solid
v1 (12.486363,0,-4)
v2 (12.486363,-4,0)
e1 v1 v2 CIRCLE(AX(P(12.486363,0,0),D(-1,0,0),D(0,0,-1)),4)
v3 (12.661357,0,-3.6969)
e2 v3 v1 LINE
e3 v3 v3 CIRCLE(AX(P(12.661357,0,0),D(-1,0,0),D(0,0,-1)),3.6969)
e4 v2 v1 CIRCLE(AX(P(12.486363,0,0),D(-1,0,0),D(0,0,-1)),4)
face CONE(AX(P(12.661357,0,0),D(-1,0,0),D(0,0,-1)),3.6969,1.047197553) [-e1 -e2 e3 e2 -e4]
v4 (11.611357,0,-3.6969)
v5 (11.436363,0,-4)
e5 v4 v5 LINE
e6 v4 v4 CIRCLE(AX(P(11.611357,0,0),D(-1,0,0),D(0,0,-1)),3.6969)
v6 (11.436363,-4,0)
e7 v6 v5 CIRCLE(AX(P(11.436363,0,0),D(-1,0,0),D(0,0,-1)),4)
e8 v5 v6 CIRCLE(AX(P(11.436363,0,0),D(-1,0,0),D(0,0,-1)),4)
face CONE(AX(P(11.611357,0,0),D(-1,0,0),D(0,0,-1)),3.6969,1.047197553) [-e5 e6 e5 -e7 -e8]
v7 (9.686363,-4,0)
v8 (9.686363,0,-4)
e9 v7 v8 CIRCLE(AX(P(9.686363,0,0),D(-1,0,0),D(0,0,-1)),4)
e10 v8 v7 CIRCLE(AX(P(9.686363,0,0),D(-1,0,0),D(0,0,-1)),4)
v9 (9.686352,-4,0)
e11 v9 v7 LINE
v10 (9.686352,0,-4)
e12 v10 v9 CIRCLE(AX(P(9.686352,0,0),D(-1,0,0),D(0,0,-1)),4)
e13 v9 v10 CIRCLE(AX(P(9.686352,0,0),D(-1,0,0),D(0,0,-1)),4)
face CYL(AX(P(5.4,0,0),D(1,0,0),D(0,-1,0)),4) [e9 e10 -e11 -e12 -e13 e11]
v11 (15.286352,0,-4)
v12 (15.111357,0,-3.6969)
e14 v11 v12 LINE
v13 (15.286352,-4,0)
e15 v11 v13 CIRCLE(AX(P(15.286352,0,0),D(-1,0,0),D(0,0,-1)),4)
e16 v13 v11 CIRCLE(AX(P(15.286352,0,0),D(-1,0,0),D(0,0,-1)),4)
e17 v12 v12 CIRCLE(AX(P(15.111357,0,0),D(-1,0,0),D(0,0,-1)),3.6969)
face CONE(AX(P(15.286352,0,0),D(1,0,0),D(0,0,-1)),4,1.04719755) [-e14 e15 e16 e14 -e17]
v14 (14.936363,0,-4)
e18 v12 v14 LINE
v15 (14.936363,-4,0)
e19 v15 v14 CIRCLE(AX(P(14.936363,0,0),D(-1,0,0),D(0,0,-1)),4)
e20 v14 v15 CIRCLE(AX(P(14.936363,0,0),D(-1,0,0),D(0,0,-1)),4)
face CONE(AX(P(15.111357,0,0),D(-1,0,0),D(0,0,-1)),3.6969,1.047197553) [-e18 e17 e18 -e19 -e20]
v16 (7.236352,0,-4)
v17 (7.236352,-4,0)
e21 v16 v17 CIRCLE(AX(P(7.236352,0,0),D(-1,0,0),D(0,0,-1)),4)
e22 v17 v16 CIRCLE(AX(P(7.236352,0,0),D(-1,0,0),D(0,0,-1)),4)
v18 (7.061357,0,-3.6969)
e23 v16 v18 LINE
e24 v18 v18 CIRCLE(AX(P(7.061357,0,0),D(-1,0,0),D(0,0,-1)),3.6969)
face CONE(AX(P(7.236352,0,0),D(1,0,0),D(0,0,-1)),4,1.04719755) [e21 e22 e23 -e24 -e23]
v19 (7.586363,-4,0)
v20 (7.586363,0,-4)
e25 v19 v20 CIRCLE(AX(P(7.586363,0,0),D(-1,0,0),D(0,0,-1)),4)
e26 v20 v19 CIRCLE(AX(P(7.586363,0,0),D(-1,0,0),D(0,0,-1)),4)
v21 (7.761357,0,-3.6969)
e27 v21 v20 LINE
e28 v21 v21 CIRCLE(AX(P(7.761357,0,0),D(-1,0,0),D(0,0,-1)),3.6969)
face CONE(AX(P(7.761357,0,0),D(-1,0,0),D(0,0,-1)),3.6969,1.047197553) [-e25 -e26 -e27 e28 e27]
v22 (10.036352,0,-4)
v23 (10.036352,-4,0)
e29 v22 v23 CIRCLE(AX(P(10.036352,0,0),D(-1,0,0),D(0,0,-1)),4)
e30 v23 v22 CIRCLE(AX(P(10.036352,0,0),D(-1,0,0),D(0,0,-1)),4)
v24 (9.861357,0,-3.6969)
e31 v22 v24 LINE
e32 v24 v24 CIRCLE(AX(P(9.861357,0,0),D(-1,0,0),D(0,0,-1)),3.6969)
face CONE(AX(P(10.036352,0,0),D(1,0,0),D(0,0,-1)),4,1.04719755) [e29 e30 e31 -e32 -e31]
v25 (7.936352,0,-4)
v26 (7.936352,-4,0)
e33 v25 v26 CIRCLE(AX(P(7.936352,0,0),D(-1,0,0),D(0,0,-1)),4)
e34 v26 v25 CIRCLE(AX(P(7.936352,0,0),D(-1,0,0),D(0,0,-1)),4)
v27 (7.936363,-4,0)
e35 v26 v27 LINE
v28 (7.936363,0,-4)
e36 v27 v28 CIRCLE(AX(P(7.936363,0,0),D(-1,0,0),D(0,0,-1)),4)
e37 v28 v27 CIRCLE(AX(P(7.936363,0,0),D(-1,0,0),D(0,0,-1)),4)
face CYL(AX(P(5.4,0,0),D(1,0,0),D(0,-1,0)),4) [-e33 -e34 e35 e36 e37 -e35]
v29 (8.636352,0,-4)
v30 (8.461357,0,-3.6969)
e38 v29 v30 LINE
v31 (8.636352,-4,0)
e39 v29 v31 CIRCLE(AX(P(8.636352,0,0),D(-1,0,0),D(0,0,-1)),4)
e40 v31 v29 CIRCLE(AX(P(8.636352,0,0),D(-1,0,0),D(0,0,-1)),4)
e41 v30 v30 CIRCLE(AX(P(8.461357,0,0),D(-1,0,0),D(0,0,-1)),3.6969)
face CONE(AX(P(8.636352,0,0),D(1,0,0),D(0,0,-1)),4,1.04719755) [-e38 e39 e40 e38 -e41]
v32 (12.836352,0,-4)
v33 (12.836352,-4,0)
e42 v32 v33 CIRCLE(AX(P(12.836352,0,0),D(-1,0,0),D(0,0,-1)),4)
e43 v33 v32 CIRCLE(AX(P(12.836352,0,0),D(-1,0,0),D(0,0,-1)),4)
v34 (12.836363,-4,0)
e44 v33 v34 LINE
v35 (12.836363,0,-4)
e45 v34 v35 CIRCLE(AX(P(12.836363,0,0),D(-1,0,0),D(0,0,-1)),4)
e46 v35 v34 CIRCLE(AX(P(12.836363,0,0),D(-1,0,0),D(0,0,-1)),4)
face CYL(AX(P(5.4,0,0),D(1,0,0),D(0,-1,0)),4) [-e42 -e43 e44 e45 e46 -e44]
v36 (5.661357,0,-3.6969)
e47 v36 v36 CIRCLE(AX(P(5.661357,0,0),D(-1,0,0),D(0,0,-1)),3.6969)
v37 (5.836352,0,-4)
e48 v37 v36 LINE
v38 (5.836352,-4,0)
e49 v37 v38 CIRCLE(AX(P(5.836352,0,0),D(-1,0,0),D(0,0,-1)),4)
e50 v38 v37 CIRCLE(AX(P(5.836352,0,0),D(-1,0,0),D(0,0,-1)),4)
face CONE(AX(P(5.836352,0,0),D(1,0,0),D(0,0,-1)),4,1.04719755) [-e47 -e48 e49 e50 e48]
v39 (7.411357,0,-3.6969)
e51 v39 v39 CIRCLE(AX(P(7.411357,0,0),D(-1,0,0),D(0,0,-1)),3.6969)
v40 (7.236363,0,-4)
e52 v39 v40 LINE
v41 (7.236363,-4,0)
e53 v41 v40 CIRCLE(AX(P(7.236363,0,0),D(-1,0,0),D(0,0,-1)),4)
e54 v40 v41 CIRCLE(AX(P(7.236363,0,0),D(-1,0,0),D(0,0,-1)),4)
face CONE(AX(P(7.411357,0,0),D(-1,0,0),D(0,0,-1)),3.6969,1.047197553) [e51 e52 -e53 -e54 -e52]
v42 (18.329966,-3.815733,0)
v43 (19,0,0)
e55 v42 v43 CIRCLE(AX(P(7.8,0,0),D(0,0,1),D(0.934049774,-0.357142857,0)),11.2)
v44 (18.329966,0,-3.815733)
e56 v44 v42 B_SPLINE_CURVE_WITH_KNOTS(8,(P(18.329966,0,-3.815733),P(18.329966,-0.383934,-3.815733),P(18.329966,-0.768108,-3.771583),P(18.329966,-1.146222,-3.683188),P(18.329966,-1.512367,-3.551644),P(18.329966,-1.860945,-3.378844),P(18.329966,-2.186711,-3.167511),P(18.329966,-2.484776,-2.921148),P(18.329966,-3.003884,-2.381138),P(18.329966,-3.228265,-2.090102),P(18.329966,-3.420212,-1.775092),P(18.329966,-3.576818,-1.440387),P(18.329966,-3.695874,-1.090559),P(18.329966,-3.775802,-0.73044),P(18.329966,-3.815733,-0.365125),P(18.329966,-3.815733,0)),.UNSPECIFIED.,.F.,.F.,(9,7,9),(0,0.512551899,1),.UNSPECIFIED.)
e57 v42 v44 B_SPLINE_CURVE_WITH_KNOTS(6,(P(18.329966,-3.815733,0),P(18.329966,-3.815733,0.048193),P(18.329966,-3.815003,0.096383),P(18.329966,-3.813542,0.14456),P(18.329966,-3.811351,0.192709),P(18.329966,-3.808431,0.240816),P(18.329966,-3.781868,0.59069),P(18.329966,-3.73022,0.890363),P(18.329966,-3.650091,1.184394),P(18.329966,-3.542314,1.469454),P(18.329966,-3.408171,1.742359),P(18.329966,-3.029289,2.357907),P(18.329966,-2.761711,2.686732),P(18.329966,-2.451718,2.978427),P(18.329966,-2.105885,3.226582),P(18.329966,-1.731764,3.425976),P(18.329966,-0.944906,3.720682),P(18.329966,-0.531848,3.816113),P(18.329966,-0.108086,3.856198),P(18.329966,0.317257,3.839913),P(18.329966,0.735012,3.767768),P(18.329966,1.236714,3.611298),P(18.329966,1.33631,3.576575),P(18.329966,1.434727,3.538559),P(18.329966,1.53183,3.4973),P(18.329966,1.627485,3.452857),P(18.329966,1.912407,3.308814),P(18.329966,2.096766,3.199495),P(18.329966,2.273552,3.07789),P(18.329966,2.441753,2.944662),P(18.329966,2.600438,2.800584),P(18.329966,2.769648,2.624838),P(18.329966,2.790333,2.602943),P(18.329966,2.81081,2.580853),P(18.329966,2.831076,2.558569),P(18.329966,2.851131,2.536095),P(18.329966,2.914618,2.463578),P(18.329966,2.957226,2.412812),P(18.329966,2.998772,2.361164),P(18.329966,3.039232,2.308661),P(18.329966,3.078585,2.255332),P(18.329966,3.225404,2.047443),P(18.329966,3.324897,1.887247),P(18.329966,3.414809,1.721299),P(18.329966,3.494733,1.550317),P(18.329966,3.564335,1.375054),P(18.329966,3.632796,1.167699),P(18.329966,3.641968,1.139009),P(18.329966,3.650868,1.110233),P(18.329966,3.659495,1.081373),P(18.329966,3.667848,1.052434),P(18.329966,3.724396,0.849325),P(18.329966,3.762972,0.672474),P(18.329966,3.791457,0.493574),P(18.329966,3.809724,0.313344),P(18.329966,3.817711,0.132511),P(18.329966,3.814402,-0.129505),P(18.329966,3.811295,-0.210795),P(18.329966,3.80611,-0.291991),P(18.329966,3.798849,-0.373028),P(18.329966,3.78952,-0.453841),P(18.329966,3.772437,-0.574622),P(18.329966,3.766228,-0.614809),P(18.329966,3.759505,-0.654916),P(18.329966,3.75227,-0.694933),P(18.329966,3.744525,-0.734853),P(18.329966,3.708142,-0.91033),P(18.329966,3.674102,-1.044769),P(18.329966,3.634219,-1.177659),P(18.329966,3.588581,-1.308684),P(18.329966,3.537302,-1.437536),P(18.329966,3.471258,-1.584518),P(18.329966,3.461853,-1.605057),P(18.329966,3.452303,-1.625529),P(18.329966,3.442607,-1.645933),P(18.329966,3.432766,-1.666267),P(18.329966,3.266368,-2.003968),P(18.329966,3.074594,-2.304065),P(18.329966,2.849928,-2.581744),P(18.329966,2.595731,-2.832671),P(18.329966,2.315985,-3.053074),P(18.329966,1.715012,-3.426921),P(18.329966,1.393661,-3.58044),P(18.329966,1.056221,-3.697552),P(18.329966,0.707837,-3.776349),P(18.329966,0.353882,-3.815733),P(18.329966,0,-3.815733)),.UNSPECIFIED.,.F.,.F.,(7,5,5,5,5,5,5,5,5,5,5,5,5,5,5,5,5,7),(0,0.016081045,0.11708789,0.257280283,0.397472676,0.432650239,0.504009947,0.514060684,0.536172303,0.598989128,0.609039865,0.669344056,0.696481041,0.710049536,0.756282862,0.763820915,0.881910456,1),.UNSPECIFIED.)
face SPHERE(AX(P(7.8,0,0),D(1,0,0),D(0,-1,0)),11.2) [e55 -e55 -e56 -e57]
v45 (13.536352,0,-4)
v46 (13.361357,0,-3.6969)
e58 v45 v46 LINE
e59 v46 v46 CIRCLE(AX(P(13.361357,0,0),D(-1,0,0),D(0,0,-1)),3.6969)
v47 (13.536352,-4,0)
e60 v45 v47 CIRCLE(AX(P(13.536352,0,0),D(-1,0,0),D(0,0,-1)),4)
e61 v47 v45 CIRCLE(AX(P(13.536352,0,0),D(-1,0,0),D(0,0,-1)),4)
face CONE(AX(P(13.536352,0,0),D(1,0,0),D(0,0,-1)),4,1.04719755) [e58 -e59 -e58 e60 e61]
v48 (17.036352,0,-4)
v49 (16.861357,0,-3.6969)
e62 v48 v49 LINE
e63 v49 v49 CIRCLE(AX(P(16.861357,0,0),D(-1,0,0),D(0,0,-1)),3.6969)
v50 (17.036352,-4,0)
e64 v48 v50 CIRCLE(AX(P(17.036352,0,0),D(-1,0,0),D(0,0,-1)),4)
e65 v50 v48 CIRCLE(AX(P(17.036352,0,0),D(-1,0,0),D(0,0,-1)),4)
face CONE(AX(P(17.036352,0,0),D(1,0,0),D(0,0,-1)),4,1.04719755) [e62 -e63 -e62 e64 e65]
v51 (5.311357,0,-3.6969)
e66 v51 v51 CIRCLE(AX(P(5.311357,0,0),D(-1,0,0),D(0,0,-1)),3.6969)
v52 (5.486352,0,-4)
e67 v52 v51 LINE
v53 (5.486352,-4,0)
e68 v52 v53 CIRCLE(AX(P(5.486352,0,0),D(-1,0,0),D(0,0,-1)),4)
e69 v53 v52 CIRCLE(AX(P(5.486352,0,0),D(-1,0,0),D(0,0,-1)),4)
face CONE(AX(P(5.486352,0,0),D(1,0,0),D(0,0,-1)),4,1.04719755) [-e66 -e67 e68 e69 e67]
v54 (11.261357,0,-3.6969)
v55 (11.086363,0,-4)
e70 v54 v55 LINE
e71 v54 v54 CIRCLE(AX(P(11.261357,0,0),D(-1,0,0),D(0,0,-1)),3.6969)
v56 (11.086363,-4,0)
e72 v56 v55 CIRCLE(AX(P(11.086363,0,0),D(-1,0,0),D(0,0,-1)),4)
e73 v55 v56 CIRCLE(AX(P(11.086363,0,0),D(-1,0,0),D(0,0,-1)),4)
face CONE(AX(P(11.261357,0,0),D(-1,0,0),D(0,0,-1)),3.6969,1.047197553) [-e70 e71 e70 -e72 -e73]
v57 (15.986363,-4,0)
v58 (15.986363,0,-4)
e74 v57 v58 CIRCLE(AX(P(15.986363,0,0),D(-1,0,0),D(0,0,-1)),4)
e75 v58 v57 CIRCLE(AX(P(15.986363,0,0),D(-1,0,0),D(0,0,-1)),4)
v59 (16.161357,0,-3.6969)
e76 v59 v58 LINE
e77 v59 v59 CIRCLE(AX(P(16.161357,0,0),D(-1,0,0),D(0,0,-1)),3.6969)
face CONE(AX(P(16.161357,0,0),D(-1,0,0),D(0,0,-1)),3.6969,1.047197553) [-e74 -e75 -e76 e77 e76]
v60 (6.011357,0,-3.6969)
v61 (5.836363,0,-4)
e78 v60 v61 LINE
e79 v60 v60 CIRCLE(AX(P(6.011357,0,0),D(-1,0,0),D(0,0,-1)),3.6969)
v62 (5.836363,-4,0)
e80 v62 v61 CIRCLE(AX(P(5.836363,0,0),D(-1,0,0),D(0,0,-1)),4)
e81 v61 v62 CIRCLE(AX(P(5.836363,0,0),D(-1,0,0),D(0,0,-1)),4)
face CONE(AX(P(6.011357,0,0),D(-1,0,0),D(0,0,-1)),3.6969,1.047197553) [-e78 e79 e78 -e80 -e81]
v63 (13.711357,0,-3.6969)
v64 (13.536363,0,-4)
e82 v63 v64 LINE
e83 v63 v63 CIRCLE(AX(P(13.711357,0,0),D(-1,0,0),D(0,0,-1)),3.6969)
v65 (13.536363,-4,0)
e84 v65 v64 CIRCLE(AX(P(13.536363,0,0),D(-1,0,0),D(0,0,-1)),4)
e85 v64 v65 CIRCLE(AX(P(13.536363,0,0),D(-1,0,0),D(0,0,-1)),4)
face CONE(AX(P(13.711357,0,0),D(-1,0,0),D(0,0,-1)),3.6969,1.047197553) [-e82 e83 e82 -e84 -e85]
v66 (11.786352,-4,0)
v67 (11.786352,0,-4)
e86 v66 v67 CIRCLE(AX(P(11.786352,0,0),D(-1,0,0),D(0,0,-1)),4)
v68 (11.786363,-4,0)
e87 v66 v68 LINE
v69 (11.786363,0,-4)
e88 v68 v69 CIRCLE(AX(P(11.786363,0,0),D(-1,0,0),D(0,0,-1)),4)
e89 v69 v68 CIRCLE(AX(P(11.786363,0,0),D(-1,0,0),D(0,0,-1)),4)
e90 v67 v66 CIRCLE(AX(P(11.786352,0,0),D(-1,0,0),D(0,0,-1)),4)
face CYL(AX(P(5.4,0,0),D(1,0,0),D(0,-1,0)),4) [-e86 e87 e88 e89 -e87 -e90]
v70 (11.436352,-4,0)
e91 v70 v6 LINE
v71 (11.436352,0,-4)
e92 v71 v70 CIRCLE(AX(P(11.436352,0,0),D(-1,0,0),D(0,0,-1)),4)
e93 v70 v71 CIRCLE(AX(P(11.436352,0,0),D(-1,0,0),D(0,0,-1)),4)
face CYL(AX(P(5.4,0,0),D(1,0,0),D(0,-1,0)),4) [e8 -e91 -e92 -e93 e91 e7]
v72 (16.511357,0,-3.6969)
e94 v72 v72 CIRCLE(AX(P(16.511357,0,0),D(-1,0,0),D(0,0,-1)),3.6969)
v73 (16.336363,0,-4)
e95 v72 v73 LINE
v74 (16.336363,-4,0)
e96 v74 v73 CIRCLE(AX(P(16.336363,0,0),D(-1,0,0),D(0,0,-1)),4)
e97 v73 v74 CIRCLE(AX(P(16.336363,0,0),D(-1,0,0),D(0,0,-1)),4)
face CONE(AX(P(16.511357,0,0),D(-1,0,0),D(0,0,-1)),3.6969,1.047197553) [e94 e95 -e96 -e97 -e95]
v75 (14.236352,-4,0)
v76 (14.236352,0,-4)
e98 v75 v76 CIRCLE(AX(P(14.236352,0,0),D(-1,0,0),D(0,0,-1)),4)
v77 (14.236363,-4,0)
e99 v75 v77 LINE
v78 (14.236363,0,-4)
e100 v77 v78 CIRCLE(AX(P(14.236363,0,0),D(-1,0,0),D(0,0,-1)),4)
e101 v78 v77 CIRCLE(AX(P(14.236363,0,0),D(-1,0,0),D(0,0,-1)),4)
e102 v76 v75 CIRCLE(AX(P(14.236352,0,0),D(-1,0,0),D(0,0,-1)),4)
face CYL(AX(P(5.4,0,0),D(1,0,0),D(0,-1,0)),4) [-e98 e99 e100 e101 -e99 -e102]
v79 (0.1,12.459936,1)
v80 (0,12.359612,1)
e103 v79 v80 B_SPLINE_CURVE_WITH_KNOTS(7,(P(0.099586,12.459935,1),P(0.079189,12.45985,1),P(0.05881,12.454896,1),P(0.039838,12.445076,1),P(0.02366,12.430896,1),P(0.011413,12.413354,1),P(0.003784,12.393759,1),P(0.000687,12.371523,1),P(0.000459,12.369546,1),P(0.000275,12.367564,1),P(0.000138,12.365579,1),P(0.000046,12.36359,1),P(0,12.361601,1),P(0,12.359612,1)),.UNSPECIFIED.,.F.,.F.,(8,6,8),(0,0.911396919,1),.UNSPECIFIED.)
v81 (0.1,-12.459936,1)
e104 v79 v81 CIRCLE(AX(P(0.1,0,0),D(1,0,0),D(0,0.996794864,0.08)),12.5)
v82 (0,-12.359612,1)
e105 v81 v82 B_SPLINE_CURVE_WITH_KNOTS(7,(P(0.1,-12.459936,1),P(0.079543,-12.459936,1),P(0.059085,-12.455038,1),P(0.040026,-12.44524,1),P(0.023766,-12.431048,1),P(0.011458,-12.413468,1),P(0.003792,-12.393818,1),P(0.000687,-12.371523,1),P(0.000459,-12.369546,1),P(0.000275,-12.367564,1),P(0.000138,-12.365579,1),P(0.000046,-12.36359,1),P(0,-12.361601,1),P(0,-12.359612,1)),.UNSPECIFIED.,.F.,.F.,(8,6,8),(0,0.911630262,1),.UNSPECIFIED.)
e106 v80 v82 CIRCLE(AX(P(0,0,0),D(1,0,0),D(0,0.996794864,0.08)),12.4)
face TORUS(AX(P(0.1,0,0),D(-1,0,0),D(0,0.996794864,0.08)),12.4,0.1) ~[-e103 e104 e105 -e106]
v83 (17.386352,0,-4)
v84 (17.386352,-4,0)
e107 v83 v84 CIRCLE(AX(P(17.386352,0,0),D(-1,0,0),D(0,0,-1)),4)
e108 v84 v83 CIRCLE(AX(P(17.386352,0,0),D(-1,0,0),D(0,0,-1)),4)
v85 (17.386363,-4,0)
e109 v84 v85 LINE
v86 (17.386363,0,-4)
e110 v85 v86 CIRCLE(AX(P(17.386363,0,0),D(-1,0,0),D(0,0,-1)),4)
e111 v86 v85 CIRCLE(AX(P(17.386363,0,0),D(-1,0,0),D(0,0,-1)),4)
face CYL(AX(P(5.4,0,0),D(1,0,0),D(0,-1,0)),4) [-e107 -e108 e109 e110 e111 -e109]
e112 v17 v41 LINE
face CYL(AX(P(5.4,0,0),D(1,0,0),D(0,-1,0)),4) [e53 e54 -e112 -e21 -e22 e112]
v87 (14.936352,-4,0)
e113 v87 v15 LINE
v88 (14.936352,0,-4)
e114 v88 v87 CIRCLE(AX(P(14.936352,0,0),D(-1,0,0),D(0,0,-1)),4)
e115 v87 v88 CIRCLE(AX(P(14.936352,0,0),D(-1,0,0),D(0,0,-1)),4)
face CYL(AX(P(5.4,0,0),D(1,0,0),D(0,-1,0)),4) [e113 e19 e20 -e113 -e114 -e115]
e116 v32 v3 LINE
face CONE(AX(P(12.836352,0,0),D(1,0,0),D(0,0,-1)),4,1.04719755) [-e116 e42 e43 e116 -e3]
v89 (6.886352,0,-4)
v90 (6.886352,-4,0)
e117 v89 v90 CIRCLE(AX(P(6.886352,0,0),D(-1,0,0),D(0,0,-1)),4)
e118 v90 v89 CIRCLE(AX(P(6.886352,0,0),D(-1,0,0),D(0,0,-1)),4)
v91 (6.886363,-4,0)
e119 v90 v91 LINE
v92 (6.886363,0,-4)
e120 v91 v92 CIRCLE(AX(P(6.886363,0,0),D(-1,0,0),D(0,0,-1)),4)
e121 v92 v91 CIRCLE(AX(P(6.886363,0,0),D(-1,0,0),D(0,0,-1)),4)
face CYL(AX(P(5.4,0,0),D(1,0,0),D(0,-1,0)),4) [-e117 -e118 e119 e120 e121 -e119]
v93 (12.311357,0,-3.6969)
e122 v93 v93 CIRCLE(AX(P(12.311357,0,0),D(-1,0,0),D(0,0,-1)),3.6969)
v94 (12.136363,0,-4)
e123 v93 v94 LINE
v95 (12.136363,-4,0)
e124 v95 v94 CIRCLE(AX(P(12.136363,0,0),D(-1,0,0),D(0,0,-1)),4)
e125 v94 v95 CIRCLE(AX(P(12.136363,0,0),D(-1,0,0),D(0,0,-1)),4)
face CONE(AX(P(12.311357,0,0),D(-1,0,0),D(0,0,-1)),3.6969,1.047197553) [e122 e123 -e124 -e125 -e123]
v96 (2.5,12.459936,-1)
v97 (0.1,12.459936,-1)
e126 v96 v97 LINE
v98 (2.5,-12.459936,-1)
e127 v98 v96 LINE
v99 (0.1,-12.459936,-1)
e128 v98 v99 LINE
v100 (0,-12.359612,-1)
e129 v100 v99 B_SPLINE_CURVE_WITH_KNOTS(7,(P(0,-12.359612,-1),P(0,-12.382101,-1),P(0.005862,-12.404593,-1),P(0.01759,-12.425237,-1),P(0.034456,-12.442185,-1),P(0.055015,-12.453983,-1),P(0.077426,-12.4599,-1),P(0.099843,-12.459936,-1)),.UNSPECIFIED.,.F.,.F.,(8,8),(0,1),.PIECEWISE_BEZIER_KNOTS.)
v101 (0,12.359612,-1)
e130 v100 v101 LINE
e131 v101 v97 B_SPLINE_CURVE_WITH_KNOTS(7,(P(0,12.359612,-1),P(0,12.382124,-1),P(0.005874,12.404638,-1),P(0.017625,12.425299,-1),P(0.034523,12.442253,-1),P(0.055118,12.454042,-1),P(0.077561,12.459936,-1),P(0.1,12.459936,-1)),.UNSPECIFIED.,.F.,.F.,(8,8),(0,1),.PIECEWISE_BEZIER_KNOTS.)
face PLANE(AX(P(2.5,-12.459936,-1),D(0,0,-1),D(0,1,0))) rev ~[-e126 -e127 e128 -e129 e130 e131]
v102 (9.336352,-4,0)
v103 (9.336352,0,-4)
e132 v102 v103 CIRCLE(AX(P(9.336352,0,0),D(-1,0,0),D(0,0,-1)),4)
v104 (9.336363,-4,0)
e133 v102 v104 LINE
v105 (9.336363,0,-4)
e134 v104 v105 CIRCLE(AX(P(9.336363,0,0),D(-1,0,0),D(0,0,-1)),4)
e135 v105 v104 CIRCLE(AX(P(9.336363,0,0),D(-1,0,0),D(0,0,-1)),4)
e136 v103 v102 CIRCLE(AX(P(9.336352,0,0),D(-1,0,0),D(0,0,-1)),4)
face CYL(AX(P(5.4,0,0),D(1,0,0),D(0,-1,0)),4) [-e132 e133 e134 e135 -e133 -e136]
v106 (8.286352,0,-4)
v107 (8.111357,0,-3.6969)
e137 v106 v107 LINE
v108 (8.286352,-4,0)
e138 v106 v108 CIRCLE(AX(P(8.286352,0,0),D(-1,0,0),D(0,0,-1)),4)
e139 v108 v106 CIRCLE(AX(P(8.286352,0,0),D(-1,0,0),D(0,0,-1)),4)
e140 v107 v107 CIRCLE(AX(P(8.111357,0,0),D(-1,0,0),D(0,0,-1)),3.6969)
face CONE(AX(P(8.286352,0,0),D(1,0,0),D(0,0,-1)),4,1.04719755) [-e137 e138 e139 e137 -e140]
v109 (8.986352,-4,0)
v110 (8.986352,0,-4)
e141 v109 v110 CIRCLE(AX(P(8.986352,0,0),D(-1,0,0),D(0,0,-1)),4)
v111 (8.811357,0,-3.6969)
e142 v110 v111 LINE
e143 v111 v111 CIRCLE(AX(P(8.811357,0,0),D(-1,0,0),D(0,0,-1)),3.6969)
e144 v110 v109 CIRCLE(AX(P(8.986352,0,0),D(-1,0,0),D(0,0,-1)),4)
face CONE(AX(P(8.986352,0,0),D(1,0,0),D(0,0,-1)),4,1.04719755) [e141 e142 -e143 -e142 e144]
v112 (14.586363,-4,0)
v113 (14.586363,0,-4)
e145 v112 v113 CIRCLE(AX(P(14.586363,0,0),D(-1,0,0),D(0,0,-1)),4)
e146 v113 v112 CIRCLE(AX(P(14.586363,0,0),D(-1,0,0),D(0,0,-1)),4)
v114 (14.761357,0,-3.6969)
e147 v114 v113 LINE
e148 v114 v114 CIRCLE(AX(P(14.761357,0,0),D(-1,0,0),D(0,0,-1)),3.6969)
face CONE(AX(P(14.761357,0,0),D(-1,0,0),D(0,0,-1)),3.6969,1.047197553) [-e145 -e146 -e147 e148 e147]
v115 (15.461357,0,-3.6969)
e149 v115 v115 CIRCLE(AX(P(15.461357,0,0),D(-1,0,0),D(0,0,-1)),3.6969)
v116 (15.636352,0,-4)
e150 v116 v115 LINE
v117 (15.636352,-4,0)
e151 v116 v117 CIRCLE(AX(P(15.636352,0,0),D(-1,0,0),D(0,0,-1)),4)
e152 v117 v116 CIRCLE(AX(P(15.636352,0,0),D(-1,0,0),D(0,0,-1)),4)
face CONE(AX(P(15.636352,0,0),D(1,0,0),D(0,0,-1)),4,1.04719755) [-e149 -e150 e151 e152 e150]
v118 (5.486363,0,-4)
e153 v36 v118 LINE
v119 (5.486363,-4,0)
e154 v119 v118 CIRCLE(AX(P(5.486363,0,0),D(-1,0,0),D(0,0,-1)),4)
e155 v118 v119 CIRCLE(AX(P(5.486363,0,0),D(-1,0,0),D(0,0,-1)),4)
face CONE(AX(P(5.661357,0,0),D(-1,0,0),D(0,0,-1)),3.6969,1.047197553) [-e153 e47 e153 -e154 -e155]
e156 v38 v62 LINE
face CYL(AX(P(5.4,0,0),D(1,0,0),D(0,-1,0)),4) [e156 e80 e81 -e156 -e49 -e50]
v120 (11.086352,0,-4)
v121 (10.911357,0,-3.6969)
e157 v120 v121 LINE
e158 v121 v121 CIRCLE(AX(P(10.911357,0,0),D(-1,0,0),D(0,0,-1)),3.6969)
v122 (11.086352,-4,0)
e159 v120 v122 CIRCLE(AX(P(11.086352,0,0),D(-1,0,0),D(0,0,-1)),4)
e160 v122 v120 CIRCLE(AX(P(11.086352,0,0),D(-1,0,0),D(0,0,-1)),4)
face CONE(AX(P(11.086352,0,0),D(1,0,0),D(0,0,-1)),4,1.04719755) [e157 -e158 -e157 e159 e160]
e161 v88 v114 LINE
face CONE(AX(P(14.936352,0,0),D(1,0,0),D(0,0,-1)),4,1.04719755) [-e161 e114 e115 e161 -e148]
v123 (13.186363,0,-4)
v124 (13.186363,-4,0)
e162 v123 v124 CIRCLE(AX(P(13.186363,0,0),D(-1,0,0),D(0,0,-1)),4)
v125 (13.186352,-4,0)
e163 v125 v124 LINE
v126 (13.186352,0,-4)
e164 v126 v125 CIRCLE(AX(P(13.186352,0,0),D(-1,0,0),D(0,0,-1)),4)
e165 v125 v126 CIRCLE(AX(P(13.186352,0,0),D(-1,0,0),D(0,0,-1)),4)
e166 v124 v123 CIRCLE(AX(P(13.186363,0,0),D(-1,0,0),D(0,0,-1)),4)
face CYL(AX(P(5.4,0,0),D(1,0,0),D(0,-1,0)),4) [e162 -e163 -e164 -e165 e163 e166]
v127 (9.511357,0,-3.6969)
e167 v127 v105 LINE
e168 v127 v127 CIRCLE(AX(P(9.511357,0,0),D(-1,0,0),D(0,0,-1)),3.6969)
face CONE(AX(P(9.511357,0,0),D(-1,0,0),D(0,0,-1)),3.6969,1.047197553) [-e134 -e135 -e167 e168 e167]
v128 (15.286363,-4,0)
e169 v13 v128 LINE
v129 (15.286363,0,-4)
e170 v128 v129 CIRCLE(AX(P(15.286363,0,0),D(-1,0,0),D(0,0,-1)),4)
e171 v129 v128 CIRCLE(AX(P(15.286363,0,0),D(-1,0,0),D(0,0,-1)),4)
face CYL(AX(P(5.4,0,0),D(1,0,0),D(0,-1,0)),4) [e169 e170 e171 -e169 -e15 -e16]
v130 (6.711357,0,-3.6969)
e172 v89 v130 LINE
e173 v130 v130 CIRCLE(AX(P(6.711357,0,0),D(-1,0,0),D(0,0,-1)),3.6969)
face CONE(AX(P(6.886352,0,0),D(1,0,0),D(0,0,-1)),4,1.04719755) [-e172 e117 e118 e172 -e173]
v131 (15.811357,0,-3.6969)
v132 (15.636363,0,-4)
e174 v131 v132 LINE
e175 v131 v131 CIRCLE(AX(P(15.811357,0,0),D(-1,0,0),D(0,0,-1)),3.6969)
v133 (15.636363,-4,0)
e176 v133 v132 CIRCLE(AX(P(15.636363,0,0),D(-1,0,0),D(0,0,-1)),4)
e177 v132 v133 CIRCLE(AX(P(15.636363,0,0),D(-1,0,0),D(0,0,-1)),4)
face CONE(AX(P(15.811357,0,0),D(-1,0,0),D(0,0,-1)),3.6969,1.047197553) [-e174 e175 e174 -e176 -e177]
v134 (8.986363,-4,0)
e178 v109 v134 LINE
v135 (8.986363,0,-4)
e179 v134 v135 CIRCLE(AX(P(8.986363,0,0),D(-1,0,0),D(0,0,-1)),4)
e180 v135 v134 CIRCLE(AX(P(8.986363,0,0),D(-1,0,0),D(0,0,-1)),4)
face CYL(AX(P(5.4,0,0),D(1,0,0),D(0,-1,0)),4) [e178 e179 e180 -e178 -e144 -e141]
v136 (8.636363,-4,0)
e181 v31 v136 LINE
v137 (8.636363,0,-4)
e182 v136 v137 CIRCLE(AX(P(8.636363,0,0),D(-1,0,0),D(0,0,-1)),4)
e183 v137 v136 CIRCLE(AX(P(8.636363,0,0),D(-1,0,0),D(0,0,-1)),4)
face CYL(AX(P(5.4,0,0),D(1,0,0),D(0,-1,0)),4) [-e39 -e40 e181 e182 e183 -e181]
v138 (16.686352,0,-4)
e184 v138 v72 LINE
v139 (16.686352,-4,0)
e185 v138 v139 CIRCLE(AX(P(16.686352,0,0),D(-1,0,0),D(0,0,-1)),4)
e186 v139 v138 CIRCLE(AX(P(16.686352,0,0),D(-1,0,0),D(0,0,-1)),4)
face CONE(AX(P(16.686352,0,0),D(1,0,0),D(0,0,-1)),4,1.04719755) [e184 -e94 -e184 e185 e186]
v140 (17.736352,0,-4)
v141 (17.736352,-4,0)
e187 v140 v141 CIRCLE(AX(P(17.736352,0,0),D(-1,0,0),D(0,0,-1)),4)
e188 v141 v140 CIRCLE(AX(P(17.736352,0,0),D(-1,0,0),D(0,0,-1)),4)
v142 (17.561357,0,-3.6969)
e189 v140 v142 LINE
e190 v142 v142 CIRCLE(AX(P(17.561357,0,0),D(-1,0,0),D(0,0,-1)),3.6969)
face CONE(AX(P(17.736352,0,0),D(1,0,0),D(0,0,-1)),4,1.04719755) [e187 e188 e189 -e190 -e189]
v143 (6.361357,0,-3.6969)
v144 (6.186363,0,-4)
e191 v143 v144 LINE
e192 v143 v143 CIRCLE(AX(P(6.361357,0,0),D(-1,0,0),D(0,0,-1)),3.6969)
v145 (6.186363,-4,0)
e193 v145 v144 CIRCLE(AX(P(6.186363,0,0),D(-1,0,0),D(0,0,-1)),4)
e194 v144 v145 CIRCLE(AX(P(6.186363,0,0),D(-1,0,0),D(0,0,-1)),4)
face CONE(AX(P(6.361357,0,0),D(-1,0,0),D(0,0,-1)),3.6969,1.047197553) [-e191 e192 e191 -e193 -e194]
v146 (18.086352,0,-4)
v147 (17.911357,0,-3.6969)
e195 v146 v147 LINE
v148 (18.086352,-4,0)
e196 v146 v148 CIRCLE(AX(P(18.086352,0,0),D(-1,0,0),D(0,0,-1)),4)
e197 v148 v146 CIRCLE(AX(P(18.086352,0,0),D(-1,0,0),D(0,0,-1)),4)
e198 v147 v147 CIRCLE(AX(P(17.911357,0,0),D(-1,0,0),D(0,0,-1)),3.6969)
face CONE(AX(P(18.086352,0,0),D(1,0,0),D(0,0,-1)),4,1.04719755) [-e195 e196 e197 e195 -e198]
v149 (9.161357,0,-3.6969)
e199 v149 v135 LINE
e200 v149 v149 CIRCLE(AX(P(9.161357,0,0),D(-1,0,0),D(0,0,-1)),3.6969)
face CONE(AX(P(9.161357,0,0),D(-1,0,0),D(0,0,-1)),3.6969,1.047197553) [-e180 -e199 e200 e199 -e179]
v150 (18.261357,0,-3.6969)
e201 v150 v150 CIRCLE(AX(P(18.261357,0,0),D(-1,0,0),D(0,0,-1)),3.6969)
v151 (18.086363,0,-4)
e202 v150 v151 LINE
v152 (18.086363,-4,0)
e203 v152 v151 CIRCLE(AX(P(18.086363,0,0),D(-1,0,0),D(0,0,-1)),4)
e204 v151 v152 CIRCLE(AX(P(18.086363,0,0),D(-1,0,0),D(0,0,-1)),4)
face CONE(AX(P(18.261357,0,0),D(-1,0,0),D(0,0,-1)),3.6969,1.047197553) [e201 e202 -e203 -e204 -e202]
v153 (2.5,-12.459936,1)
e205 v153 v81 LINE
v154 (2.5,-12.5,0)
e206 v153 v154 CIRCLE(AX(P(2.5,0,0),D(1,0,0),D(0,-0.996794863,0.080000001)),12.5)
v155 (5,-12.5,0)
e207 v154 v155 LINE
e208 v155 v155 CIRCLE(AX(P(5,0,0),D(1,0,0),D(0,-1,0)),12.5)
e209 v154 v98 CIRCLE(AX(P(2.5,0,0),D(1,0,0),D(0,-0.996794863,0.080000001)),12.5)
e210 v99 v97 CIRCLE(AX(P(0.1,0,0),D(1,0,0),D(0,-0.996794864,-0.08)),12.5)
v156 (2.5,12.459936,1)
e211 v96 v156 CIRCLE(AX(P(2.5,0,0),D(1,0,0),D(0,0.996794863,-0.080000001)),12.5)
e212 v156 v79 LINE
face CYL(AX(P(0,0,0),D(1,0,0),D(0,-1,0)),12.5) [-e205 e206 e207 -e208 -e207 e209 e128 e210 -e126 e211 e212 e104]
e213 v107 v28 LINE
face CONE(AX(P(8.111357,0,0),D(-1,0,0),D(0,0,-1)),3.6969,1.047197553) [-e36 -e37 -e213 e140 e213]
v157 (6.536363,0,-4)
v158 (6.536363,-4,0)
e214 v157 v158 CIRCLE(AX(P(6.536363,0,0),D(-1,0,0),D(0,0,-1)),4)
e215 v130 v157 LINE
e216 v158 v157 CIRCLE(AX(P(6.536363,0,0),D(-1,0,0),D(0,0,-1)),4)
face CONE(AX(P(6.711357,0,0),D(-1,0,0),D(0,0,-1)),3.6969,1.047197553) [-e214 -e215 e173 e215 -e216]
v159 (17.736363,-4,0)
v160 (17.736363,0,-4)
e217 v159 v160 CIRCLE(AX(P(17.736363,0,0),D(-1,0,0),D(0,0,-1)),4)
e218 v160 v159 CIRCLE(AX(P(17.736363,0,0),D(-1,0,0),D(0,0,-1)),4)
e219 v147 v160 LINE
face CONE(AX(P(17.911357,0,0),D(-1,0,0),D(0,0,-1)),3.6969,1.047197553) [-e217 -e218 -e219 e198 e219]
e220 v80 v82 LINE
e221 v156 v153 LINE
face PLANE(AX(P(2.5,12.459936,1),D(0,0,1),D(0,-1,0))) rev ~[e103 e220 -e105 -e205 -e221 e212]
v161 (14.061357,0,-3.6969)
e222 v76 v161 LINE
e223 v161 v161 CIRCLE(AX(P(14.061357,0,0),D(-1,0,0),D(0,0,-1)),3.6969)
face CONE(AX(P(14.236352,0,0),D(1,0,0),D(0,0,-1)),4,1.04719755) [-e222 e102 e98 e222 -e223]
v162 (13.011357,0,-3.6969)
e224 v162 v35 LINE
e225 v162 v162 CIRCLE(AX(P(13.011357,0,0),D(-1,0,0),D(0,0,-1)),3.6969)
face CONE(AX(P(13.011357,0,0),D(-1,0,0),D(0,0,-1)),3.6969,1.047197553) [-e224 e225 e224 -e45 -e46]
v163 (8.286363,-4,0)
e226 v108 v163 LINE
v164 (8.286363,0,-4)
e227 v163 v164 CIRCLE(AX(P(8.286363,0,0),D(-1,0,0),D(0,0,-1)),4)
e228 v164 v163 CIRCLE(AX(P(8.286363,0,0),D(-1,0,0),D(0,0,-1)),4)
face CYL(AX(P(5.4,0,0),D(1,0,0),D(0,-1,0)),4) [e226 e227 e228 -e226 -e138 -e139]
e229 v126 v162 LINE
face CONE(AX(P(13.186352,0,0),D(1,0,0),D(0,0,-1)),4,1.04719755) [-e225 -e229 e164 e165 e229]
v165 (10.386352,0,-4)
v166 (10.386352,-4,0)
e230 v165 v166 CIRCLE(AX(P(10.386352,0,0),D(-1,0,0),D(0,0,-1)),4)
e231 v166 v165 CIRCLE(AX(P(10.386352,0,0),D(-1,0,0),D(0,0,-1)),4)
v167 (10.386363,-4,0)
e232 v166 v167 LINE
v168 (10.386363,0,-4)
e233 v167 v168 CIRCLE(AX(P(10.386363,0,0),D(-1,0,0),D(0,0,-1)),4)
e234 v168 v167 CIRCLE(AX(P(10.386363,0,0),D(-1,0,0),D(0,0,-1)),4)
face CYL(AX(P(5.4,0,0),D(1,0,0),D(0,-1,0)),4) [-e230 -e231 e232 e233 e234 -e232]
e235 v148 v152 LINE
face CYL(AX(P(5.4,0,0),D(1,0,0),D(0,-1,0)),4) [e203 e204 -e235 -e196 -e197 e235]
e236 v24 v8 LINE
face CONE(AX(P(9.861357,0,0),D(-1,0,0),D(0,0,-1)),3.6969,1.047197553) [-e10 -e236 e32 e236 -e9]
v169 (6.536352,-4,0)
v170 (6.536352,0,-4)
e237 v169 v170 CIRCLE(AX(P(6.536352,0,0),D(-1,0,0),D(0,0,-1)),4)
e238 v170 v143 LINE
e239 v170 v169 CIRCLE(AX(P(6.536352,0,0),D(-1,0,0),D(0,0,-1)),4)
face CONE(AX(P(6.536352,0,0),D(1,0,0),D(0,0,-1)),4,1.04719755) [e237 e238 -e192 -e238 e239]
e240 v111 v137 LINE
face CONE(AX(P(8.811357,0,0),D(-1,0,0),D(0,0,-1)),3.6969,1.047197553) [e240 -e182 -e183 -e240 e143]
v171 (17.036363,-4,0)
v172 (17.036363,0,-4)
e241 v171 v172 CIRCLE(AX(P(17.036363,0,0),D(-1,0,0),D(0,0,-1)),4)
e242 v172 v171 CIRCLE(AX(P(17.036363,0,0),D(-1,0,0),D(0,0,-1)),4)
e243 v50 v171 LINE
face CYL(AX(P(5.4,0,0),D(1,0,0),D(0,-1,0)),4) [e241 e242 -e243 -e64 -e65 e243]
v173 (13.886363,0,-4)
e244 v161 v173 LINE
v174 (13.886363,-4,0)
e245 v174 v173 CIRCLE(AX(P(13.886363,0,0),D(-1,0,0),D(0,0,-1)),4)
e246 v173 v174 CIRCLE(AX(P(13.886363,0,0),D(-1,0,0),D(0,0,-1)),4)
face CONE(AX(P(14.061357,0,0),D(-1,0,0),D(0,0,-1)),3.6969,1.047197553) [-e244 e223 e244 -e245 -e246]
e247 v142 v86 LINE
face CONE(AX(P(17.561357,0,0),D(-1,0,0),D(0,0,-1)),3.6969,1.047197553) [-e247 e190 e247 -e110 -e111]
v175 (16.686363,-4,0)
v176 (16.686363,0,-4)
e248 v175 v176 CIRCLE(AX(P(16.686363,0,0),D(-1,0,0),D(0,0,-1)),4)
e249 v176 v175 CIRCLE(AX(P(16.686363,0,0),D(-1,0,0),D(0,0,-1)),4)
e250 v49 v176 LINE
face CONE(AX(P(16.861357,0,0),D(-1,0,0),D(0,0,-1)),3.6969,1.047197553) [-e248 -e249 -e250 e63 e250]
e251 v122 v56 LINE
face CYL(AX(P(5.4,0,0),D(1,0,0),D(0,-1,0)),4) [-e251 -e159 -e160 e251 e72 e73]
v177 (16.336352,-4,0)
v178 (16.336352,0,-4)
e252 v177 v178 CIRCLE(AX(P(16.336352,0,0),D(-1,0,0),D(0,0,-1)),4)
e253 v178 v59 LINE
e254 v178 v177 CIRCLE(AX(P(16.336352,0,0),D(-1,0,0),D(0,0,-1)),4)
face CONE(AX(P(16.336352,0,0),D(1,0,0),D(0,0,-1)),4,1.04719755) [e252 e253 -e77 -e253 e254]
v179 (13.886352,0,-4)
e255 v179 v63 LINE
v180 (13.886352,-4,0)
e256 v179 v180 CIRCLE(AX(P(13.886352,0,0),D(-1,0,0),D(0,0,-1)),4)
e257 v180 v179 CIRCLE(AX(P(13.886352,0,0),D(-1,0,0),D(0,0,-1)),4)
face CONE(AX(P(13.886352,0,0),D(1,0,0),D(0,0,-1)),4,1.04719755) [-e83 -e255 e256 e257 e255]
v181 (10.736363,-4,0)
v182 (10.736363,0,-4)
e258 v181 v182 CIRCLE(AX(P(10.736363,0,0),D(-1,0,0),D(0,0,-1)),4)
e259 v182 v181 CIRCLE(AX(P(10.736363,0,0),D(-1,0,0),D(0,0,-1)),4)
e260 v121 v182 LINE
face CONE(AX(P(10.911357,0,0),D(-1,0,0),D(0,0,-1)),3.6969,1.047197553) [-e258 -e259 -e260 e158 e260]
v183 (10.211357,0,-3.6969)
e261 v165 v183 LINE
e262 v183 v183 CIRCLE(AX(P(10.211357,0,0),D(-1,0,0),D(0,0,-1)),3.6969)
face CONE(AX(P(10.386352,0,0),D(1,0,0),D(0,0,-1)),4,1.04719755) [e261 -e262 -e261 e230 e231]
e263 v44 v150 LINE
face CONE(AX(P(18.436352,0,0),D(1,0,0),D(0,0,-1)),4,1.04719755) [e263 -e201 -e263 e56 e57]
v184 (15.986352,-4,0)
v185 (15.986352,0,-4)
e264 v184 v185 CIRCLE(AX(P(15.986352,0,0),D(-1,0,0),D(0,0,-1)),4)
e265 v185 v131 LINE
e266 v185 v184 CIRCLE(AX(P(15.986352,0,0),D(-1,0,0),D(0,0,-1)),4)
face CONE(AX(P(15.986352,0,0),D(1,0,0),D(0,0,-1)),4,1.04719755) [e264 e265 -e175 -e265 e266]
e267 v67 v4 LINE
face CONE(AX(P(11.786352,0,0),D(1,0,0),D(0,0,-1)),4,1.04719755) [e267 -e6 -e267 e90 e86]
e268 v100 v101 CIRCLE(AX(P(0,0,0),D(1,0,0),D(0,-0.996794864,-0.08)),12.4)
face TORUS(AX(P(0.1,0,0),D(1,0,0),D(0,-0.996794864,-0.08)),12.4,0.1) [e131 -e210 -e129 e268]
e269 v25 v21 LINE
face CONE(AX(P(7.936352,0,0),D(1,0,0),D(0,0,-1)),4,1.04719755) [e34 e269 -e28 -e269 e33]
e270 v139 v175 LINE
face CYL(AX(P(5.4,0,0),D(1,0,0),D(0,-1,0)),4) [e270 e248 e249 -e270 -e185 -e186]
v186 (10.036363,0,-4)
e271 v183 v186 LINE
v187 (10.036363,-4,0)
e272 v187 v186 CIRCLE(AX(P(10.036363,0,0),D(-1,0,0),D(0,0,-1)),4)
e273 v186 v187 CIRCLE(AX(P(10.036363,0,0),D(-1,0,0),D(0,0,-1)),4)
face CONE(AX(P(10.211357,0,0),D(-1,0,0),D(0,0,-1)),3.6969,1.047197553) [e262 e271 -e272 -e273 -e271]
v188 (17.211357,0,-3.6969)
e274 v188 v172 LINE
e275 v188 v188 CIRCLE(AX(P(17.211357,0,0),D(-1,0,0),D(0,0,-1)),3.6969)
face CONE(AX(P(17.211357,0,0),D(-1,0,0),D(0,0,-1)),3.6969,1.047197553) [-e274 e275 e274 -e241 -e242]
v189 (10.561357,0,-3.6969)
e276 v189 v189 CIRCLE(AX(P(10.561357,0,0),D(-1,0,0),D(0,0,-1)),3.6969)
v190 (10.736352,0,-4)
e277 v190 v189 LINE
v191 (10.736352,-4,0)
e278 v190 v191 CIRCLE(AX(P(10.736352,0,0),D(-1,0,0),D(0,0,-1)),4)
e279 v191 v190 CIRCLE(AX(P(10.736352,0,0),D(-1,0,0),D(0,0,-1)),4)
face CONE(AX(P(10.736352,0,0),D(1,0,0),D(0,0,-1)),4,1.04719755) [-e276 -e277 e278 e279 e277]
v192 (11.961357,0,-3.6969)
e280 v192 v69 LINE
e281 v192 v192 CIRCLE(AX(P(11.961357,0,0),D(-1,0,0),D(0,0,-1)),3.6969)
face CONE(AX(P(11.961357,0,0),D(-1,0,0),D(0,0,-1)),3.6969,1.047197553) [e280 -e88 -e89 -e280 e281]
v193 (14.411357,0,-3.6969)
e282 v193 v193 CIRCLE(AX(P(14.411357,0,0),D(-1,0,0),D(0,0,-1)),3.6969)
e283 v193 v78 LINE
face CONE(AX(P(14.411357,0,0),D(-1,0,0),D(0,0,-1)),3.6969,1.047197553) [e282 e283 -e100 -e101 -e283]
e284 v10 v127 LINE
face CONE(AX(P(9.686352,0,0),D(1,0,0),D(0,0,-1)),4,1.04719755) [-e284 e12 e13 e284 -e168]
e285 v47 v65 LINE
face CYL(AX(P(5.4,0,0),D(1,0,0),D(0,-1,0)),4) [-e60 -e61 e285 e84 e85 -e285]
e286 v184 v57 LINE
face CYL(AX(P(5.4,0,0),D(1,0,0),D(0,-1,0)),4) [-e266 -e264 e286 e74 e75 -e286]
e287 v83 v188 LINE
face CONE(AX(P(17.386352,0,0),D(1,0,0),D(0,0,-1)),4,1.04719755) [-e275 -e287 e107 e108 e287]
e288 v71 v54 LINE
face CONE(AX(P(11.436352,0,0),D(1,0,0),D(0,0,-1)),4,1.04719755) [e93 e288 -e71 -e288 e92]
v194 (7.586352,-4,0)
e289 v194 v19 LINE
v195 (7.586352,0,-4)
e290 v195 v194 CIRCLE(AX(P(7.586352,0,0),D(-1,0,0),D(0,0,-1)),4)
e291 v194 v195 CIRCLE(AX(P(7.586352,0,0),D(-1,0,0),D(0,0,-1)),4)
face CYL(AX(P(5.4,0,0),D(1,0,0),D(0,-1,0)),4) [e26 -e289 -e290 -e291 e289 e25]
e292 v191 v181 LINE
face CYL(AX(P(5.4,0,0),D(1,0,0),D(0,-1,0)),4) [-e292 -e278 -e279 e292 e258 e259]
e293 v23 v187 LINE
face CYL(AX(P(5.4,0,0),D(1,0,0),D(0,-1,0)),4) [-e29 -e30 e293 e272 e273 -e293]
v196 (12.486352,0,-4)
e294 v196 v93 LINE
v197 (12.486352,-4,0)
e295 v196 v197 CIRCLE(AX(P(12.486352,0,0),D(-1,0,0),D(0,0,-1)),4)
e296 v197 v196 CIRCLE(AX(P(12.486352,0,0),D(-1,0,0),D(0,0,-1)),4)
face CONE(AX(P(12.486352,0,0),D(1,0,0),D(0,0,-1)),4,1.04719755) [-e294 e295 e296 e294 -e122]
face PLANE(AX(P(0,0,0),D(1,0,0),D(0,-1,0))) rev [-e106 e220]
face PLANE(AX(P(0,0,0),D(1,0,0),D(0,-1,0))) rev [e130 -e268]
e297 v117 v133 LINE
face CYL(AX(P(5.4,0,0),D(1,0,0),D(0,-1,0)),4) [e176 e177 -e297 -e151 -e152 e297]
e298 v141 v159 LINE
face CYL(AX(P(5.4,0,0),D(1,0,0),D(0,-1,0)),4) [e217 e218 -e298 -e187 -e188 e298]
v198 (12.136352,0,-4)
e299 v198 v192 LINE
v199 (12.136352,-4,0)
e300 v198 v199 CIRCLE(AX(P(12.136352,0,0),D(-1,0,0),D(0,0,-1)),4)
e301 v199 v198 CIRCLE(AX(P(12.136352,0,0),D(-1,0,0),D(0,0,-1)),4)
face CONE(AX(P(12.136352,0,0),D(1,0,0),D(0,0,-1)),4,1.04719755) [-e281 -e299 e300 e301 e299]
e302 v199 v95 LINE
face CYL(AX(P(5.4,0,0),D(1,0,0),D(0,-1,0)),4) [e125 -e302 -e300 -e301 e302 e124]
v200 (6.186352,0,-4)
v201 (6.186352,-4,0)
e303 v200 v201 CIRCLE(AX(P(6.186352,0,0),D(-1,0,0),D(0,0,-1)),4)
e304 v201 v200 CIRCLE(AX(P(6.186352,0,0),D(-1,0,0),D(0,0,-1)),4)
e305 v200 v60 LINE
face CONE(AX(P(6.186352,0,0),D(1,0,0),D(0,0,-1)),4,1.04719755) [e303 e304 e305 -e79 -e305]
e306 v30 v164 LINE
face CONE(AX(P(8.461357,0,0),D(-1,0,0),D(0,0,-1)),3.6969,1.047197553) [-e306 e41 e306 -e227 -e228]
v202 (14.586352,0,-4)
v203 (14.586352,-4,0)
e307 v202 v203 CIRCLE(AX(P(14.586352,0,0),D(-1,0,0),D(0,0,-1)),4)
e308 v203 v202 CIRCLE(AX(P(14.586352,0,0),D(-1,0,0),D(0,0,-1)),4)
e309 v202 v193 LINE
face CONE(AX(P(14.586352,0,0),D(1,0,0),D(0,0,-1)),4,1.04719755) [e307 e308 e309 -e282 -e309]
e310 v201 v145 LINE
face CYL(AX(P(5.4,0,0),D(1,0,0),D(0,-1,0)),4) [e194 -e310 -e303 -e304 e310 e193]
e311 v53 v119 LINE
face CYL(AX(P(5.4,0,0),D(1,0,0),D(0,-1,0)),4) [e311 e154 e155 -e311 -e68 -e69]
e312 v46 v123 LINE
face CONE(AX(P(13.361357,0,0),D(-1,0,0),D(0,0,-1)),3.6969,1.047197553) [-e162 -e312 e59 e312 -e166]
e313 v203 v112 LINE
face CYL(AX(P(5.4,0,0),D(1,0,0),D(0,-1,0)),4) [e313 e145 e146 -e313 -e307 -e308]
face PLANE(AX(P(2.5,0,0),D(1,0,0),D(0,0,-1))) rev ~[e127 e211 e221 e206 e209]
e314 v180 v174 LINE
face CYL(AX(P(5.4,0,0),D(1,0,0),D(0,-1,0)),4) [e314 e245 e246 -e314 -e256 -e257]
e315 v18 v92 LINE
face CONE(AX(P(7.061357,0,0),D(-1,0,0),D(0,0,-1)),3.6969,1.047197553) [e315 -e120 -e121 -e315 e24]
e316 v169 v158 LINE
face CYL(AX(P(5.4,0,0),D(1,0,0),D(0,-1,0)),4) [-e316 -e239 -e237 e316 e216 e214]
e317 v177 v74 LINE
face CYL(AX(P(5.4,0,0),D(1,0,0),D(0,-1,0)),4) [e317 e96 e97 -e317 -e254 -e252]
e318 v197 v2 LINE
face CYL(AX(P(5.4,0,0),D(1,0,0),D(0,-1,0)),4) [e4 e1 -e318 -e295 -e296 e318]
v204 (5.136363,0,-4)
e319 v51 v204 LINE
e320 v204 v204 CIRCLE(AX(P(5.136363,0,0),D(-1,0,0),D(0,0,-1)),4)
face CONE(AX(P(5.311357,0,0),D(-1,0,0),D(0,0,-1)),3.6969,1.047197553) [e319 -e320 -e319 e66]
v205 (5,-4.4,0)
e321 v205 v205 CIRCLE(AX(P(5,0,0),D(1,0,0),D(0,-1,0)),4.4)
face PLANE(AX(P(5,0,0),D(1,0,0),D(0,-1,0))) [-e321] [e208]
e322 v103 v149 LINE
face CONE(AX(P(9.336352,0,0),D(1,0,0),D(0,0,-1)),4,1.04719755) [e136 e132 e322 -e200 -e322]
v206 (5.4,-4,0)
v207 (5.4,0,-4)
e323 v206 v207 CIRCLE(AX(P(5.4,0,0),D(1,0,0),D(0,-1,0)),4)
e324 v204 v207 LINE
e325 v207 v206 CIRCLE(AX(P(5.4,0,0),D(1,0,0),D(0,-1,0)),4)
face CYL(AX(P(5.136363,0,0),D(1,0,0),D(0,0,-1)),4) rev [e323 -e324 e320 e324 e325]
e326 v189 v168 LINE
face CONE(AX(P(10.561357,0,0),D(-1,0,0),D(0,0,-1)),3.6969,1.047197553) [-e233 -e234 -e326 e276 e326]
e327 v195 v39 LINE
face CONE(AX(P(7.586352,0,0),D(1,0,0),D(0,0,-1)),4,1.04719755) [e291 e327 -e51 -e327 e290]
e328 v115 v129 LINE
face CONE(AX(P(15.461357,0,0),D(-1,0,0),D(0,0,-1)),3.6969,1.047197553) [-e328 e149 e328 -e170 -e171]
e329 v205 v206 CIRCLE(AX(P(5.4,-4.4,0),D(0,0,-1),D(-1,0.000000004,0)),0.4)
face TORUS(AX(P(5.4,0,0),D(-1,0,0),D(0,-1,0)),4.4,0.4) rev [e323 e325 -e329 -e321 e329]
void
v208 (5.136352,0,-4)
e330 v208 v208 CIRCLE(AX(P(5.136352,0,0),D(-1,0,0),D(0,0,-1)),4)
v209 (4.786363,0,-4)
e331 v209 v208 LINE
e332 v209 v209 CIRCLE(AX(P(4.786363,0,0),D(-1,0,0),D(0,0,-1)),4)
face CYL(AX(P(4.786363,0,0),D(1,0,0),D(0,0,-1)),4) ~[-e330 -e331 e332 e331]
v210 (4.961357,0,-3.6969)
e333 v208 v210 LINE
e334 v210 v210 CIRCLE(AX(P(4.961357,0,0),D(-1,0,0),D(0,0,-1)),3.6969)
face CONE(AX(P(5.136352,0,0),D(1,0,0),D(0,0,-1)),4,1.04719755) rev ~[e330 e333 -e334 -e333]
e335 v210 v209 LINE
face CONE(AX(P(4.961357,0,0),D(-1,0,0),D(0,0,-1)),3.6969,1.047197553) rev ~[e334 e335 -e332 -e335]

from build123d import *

# Parameters (mm, degrees)
CUT_EXTRUDE_START      = -2.5
CUT_EXTRUDE_1_DEPTH    = 2.5
FILLET_1_R             = 0.1
PATTERN_LINEAR_1_COUNT = 39
PATTERN_LINEAR_1_PITCH = 0.35


with BuildPart() as part:
    # 草图1 → Revolve 584 (revolve)
    with BuildSketch(Plane.XY, mode=Mode.PRIVATE) as revolve_584_sk:
        with BuildLine():
            Line((0, 0), (0, 12.5))
            Line((0, 12.5), (5, 12.5))
            Line((5, 12.5), (5, 4.4))
            ThreePointArc((5, 4.4), (5.117157288, 4.117157288), (5.4, 4))
            Line((5.4, 4), (18.261357464, 4))
            ThreePointArc((18.261357464, 4), (18.813791436, 2.033813708), (19, 0))
            Line((19, 0), (0, 0))
        make_face()
    revolve(revolve_584_sk.sketch.rotate(Axis((0, 0, 0), (1, 0, 0)), 180), axis=Axis((0, 0, 0), (1, 0, 0)))

    # 草图2 → 切除-拉伸1 (cut)
    with BuildSketch(Plane.ZY.offset(CUT_EXTRUDE_START)):
        with BuildLine():
            Line((1, 12.459935794), (1, -12.459935794))
            ThreePointArc((1, -12.459935794), (0, -12.5), (-1, -12.459935794))
            Line((-1, -12.459935794), (-1, 12.459935794))
            ThreePointArc((-1, 12.459935794), (0, 12.5), (1, 12.459935794))
        make_face()
    extrude(amount=CUT_EXTRUDE_1_DEPTH, mode=Mode.SUBTRACT)

    # 圆角1
    fillet_1_edges = [part.edges().sort_by_distance(p)[0] for p in [
        (0, 0, -12.5),
        (0, 0, 12.5),
    ]]
    fillet(fillet_1_edges, radius=FILLET_1_R)

    # 草图3 → 切除-旋转1 (revolve, cut)
    with BuildSketch(Plane.XY, mode=Mode.PRIVATE) as cut_revolve_1_sk:
        Polygon((18.086362598, 4), (18.436352331, 4), (18.261357464, 3.6969), align=None)
    cut_revolve_1 = revolve(cut_revolve_1_sk.sketch.rotate(Axis((0, 0, 0), (-1, 0, 0)), 90), axis=Axis((0, 0, 0), (-1, 0, 0)), mode=Mode.SUBTRACT)

    # 阵列(线性)1: 切除-旋转1 ×39
    with Locations(*[(-i * PATTERN_LINEAR_1_PITCH, 0, 0) for i in range(1, PATTERN_LINEAR_1_COUNT)]):
        add(cut_revolve_1, mode=Mode.SUBTRACT)


solid = part.part
